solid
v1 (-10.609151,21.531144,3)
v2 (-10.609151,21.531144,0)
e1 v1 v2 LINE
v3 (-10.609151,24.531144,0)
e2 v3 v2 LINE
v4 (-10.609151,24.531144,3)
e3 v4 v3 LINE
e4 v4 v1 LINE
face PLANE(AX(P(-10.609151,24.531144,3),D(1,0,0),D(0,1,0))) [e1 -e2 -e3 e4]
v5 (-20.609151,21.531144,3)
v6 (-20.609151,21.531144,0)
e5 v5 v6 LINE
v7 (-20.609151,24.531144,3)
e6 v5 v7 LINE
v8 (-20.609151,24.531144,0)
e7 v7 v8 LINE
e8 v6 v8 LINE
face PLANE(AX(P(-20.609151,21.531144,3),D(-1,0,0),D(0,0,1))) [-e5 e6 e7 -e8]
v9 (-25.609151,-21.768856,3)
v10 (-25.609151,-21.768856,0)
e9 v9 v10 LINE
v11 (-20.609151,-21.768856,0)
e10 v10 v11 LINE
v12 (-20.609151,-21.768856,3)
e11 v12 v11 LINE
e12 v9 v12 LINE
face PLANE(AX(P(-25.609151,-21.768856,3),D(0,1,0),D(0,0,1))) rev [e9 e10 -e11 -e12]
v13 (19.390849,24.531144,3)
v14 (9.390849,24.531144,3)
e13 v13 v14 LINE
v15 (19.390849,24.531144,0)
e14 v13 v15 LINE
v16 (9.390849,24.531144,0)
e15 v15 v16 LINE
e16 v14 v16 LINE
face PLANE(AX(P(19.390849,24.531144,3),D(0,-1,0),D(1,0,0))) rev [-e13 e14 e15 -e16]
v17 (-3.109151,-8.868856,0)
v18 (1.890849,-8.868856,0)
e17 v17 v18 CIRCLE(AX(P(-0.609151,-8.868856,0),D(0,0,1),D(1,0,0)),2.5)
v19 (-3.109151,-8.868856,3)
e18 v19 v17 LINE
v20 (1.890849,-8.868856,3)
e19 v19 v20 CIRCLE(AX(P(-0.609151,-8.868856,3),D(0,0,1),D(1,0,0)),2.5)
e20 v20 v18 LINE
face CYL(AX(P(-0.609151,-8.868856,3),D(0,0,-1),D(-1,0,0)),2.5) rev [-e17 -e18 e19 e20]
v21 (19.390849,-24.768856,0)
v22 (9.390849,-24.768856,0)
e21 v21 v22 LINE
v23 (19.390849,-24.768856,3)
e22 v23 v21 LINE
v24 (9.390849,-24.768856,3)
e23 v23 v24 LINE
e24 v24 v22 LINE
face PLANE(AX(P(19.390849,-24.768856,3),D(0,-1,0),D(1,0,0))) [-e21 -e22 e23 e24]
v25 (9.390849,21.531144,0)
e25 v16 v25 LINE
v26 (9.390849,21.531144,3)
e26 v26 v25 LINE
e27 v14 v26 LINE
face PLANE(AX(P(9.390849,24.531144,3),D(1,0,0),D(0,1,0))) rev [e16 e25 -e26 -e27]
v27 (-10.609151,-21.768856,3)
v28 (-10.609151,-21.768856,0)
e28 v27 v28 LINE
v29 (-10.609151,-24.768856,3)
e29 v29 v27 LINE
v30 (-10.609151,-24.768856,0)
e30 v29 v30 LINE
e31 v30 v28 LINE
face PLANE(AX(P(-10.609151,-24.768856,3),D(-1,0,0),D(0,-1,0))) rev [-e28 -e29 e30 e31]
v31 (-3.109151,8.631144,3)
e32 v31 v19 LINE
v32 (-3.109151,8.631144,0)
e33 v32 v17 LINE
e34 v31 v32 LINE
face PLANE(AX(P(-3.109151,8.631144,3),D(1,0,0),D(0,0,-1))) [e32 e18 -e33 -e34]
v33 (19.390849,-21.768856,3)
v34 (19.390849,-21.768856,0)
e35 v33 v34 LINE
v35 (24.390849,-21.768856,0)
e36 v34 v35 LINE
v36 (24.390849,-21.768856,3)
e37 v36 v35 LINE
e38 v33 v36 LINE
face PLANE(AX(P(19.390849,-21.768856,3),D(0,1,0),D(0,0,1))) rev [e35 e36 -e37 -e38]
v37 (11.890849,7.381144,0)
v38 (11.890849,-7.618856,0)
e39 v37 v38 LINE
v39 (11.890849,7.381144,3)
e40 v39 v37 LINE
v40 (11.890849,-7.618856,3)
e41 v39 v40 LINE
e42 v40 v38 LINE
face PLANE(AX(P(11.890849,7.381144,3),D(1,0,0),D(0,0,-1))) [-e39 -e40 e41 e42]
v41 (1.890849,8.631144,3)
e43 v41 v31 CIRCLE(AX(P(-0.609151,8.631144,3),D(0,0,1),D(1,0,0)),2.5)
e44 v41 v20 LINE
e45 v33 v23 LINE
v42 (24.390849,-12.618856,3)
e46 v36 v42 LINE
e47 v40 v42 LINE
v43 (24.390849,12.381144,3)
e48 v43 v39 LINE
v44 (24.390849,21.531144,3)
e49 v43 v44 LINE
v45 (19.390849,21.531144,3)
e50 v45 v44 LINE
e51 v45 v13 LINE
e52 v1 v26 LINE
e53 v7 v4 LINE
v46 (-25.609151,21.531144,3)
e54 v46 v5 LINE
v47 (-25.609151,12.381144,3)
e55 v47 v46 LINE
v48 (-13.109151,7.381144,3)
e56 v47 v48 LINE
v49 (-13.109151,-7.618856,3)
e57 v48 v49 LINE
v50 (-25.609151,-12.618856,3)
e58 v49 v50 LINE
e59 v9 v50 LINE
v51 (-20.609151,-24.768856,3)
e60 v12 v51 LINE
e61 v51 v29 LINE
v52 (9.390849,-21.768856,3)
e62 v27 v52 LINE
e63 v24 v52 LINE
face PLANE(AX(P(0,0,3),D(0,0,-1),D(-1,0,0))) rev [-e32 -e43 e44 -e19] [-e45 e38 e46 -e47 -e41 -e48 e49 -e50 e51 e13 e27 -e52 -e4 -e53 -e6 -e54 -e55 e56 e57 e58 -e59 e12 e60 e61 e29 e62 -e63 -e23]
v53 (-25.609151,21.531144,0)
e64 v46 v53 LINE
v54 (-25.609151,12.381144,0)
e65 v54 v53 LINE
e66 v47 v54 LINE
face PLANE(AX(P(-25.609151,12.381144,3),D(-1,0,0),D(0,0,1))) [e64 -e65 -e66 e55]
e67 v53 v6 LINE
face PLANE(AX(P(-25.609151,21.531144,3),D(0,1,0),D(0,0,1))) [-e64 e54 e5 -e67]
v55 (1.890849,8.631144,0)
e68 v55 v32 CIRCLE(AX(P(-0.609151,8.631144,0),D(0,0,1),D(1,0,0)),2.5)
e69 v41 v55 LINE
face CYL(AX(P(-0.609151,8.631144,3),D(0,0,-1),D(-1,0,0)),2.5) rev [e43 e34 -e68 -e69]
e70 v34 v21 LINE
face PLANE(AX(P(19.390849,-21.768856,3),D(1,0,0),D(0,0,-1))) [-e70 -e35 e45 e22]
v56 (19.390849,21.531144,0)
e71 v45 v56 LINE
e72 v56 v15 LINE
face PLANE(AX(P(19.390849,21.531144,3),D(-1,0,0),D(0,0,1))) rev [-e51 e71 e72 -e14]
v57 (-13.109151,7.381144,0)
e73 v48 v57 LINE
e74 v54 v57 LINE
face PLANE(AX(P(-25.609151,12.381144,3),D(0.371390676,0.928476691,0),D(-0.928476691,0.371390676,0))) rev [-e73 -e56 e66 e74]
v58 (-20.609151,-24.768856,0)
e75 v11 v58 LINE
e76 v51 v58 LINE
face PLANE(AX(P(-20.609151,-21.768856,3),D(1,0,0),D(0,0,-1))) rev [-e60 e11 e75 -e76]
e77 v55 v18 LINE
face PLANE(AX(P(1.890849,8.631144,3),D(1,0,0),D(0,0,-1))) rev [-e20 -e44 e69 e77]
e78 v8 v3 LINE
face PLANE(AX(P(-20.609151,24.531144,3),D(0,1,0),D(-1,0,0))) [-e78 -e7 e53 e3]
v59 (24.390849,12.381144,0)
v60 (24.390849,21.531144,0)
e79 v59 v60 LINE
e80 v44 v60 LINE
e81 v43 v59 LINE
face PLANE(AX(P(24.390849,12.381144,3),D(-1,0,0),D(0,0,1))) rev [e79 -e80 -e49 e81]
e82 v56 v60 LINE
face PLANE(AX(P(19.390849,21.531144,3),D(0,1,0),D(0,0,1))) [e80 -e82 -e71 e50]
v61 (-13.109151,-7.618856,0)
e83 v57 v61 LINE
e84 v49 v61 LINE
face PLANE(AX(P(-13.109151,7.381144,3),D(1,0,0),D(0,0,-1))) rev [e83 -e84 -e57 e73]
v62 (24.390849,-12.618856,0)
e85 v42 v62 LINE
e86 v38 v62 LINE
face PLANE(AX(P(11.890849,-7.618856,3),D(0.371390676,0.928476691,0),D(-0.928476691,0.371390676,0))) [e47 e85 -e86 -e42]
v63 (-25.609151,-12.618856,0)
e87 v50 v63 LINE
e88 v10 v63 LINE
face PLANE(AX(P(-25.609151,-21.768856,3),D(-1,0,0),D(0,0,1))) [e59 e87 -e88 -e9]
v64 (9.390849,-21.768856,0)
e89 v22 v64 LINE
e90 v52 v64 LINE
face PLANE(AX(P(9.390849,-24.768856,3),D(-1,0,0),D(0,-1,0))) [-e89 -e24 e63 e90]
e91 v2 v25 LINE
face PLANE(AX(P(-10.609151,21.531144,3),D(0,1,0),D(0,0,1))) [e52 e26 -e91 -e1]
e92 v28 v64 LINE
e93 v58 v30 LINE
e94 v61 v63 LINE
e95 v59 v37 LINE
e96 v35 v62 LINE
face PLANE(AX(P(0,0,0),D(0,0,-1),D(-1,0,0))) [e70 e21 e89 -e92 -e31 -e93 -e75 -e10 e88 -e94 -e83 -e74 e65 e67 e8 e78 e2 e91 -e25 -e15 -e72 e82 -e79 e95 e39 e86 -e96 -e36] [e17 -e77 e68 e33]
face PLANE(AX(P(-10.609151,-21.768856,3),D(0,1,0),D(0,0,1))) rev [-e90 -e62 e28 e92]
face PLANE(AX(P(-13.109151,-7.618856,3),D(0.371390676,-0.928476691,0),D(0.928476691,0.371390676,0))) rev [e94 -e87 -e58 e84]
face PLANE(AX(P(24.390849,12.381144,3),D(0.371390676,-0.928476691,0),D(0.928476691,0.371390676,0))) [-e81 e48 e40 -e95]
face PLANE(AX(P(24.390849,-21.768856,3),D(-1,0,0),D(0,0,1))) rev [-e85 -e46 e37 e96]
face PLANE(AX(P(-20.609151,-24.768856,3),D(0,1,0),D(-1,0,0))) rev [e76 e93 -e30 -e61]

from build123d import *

# Parameters (mm, degrees)
EXTRUDE_1_DEPTH = 3


with BuildPart() as part:
    # 草图1 → 凸台-拉伸1 (new body)
    with BuildSketch(Plane.XY):
        Polygon((-25.609151467, -21.768855911), (-20.609151467, -21.768855911), (-20.609151467, -24.768855911), (-10.609151467, -24.768855911), (-10.609151467, -21.768855911), (9.390848533, -21.768855911), (9.390848533, -24.768855911), (19.390848533, -24.768855911), (19.390848533, -21.768855911), (24.390848533, -21.768855911), (24.390848533, -12.618855911), (11.890848533, -7.618855911), (11.890848533, 7.381144089), (24.390848533, 12.381144089), (24.390848533, 21.531144089), (19.390848533, 21.531144089), (19.390848533, 24.531144089), (9.390848533, 24.531144089), (9.390848533, 21.531144089), (-10.609151467, 21.531144089), (-10.609151467, 24.531144089), (-20.609151467, 24.531144089), (-20.609151467, 21.531144089), (-25.609151467, 21.531144089), (-25.609151467, 12.381144089), (-13.109151467, 7.381144089), (-13.109151467, -7.618855911), (-25.609151467, -12.618855911), align=None)
        with BuildLine():
            Line((1.890848533, 8.631144089), (1.890848533, -8.868855911))
            ThreePointArc((1.890848533, -8.868855911), (-0.609151467, -11.368855911), (-3.109151467, -8.868855911))
            Line((-3.109151467, -8.868855911), (-3.109151467, 8.631144089))
            ThreePointArc((-3.109151467, 8.631144089), (-0.609151467, 11.131144089), (1.890848533, 8.631144089))
        make_face(mode=Mode.SUBTRACT)
    extrude(amount=EXTRUDE_1_DEPTH)


solid = part.part
